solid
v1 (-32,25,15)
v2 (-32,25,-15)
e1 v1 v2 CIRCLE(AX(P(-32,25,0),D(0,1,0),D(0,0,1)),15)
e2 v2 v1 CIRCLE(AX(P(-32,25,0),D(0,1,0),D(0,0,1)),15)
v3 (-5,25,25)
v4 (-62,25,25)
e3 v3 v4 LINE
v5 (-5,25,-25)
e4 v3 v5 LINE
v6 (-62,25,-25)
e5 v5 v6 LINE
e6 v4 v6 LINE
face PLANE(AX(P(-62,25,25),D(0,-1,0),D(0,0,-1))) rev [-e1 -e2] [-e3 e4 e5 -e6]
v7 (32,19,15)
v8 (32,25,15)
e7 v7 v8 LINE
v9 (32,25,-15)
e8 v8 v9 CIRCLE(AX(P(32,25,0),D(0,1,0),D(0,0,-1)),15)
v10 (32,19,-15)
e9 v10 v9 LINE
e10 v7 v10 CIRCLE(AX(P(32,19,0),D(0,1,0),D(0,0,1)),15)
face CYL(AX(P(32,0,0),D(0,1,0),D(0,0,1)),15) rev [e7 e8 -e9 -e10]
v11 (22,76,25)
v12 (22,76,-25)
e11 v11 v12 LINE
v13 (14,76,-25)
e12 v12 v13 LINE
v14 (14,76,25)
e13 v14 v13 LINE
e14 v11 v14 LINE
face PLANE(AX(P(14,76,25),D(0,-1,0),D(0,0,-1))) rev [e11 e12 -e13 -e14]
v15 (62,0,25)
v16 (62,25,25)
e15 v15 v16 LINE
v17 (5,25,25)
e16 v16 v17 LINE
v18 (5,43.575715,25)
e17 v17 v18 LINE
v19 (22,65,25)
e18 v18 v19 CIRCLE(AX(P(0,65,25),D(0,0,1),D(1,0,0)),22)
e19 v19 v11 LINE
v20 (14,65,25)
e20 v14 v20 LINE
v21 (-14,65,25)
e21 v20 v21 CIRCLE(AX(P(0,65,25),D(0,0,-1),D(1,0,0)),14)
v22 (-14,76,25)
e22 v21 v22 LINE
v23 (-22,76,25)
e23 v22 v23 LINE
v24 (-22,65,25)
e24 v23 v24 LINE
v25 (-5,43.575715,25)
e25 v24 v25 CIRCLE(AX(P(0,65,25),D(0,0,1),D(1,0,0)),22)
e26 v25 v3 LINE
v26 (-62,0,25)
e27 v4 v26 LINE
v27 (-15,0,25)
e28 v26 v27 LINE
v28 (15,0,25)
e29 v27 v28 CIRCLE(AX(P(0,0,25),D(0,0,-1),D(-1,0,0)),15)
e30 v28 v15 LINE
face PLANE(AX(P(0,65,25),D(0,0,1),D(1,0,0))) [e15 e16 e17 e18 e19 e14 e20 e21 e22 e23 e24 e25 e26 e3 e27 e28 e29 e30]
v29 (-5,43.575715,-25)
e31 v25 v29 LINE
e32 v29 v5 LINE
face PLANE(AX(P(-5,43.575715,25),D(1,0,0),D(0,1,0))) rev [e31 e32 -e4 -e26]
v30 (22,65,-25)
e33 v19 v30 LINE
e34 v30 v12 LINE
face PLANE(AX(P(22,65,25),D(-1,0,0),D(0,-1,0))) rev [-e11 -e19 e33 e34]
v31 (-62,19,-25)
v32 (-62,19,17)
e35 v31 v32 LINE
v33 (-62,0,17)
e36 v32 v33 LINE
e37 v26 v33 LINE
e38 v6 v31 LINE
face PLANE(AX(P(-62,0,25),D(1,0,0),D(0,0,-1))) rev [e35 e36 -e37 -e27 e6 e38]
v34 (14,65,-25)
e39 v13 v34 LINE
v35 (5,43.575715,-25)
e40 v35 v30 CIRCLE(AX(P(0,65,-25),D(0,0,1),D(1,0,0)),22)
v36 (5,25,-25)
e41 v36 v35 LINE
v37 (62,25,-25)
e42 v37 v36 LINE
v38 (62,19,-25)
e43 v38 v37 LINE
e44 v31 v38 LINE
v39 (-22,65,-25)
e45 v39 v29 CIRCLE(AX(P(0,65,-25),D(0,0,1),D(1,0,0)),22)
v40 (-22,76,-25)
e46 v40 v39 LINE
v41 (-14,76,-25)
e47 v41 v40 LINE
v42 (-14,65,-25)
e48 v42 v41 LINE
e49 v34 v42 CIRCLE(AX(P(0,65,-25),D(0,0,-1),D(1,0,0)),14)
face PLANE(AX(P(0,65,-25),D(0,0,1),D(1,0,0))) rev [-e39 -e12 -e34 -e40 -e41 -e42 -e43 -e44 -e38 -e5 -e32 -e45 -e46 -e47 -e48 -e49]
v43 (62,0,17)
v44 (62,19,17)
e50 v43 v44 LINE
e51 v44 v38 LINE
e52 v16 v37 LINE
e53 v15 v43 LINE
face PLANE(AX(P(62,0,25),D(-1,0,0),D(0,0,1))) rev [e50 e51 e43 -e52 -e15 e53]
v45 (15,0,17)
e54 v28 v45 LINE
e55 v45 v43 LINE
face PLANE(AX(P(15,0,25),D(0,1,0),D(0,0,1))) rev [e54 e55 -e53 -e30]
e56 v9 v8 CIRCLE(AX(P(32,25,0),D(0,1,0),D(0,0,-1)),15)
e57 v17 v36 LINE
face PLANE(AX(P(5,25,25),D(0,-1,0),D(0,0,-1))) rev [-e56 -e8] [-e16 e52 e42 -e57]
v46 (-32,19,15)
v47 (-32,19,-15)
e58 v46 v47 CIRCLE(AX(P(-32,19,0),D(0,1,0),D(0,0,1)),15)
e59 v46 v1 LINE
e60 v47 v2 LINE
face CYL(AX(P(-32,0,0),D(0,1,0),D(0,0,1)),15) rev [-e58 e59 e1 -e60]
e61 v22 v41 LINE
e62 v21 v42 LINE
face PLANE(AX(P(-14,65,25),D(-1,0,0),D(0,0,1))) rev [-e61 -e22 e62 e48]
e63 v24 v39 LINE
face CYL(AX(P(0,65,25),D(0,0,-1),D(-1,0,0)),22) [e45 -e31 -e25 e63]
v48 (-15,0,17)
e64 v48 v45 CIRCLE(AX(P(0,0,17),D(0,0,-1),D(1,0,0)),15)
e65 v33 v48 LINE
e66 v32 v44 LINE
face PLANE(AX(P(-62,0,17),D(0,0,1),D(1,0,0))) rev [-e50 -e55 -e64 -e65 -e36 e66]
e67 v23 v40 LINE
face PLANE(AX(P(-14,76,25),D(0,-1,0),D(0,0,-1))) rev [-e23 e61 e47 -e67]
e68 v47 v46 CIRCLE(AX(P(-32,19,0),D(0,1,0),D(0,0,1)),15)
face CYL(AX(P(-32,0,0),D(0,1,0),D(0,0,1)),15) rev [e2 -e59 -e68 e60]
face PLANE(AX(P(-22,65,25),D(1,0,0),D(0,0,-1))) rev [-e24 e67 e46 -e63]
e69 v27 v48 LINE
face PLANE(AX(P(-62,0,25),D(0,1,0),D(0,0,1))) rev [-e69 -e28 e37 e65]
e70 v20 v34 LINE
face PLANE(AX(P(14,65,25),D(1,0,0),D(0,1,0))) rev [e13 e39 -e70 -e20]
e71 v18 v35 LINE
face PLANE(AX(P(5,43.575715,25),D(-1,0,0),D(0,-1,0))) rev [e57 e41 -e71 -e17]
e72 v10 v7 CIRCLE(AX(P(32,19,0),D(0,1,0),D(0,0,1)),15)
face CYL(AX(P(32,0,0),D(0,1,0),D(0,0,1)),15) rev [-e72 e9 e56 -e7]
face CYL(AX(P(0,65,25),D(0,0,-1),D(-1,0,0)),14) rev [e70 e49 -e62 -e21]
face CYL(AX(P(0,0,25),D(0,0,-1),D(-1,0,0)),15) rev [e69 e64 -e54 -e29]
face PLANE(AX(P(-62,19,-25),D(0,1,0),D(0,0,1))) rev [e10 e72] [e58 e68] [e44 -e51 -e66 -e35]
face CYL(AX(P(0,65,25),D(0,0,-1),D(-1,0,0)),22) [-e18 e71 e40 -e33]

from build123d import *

# Parameters (mm, degrees)
BRACKET_BODY_DEPTH         = 25
CRADLE_SLOT_CUT_DEPTH      = 148.57032222
CRADLE_SLOT_CUT_DEPTH_BACK = 148.57032222
CRADLE_SLOT_SKETCH_W       = 42
CRADLE_SLOT_SKETCH_H       = 19
BASE_CUT_OUT_SKETCH_R      = 15
BASE_CUT_OUTS_DEPTH        = 85.083292038


with BuildPart() as part:
    # Bracket Profile Sketch → Bracket Body (new, symmetric)
    with BuildSketch(Plane.XY):
        with BuildLine():
            Line((-62, 0), (-15, 0))
            ThreePointArc((-15, 0), (0, 15), (15, 0))
            Line((15, 0), (62, 0))
            Line((62, 0), (62, 25))
            Line((62, 25), (5, 25))
            Line((5, 25), (5, 43.575714714))
            ThreePointArc((5, 43.575714714), (17.23368794, 51.325205669), (22, 65))
            Line((22, 65), (22, 76))
            Line((22, 76), (14, 76))
            Line((14, 76), (14, 65))
            ThreePointArc((14, 65), (0, 51), (-14, 65))
            Line((-14, 65), (-14, 76))
            Line((-14, 76), (-22, 76))
            Line((-22, 76), (-22, 65))
            ThreePointArc((-22, 65), (-17.23368794, 51.325205669), (-5, 43.575714714))
            Line((-5, 43.575714714), (-5, 25))
            Line((-5, 25), (-62, 25))
            Line((-62, 25), (-62, 0))
        make_face()
    extrude(amount=BRACKET_BODY_DEPTH, both=True)

    # Cradle Slot Sketch → Cradle Slot Cut (cut, two sides: drawn at the far end of the back side and taken through both)
    with BuildSketch(Plane(origin=(62, 0, 0), x_dir=(0, 0, -1), z_dir=(1, 0, 0)).offset(-CRADLE_SLOT_CUT_DEPTH_BACK)):
        with Locations((4, 9.5)):
            Rectangle(CRADLE_SLOT_SKETCH_W, CRADLE_SLOT_SKETCH_H)
    extrude(amount=CRADLE_SLOT_CUT_DEPTH + CRADLE_SLOT_CUT_DEPTH_BACK, mode=Mode.SUBTRACT)

    # Base Cut-Out Sketch → Base Cut-Outs (cut, through all)
    with BuildSketch(Plane(origin=(0, 25, 0), x_dir=(1, 0, 0), z_dir=(0, 1, 0))):
        with Locations(Location((-32, 0, 0), (0, 0, 270))):
            Circle(BASE_CUT_OUT_SKETCH_R)
        with Locations(Location((32, 0, 0), (0, 0, 270))):
            Circle(BASE_CUT_OUT_SKETCH_R)
    extrude(amount=-BASE_CUT_OUTS_DEPTH, mode=Mode.SUBTRACT)


solid = part.part
